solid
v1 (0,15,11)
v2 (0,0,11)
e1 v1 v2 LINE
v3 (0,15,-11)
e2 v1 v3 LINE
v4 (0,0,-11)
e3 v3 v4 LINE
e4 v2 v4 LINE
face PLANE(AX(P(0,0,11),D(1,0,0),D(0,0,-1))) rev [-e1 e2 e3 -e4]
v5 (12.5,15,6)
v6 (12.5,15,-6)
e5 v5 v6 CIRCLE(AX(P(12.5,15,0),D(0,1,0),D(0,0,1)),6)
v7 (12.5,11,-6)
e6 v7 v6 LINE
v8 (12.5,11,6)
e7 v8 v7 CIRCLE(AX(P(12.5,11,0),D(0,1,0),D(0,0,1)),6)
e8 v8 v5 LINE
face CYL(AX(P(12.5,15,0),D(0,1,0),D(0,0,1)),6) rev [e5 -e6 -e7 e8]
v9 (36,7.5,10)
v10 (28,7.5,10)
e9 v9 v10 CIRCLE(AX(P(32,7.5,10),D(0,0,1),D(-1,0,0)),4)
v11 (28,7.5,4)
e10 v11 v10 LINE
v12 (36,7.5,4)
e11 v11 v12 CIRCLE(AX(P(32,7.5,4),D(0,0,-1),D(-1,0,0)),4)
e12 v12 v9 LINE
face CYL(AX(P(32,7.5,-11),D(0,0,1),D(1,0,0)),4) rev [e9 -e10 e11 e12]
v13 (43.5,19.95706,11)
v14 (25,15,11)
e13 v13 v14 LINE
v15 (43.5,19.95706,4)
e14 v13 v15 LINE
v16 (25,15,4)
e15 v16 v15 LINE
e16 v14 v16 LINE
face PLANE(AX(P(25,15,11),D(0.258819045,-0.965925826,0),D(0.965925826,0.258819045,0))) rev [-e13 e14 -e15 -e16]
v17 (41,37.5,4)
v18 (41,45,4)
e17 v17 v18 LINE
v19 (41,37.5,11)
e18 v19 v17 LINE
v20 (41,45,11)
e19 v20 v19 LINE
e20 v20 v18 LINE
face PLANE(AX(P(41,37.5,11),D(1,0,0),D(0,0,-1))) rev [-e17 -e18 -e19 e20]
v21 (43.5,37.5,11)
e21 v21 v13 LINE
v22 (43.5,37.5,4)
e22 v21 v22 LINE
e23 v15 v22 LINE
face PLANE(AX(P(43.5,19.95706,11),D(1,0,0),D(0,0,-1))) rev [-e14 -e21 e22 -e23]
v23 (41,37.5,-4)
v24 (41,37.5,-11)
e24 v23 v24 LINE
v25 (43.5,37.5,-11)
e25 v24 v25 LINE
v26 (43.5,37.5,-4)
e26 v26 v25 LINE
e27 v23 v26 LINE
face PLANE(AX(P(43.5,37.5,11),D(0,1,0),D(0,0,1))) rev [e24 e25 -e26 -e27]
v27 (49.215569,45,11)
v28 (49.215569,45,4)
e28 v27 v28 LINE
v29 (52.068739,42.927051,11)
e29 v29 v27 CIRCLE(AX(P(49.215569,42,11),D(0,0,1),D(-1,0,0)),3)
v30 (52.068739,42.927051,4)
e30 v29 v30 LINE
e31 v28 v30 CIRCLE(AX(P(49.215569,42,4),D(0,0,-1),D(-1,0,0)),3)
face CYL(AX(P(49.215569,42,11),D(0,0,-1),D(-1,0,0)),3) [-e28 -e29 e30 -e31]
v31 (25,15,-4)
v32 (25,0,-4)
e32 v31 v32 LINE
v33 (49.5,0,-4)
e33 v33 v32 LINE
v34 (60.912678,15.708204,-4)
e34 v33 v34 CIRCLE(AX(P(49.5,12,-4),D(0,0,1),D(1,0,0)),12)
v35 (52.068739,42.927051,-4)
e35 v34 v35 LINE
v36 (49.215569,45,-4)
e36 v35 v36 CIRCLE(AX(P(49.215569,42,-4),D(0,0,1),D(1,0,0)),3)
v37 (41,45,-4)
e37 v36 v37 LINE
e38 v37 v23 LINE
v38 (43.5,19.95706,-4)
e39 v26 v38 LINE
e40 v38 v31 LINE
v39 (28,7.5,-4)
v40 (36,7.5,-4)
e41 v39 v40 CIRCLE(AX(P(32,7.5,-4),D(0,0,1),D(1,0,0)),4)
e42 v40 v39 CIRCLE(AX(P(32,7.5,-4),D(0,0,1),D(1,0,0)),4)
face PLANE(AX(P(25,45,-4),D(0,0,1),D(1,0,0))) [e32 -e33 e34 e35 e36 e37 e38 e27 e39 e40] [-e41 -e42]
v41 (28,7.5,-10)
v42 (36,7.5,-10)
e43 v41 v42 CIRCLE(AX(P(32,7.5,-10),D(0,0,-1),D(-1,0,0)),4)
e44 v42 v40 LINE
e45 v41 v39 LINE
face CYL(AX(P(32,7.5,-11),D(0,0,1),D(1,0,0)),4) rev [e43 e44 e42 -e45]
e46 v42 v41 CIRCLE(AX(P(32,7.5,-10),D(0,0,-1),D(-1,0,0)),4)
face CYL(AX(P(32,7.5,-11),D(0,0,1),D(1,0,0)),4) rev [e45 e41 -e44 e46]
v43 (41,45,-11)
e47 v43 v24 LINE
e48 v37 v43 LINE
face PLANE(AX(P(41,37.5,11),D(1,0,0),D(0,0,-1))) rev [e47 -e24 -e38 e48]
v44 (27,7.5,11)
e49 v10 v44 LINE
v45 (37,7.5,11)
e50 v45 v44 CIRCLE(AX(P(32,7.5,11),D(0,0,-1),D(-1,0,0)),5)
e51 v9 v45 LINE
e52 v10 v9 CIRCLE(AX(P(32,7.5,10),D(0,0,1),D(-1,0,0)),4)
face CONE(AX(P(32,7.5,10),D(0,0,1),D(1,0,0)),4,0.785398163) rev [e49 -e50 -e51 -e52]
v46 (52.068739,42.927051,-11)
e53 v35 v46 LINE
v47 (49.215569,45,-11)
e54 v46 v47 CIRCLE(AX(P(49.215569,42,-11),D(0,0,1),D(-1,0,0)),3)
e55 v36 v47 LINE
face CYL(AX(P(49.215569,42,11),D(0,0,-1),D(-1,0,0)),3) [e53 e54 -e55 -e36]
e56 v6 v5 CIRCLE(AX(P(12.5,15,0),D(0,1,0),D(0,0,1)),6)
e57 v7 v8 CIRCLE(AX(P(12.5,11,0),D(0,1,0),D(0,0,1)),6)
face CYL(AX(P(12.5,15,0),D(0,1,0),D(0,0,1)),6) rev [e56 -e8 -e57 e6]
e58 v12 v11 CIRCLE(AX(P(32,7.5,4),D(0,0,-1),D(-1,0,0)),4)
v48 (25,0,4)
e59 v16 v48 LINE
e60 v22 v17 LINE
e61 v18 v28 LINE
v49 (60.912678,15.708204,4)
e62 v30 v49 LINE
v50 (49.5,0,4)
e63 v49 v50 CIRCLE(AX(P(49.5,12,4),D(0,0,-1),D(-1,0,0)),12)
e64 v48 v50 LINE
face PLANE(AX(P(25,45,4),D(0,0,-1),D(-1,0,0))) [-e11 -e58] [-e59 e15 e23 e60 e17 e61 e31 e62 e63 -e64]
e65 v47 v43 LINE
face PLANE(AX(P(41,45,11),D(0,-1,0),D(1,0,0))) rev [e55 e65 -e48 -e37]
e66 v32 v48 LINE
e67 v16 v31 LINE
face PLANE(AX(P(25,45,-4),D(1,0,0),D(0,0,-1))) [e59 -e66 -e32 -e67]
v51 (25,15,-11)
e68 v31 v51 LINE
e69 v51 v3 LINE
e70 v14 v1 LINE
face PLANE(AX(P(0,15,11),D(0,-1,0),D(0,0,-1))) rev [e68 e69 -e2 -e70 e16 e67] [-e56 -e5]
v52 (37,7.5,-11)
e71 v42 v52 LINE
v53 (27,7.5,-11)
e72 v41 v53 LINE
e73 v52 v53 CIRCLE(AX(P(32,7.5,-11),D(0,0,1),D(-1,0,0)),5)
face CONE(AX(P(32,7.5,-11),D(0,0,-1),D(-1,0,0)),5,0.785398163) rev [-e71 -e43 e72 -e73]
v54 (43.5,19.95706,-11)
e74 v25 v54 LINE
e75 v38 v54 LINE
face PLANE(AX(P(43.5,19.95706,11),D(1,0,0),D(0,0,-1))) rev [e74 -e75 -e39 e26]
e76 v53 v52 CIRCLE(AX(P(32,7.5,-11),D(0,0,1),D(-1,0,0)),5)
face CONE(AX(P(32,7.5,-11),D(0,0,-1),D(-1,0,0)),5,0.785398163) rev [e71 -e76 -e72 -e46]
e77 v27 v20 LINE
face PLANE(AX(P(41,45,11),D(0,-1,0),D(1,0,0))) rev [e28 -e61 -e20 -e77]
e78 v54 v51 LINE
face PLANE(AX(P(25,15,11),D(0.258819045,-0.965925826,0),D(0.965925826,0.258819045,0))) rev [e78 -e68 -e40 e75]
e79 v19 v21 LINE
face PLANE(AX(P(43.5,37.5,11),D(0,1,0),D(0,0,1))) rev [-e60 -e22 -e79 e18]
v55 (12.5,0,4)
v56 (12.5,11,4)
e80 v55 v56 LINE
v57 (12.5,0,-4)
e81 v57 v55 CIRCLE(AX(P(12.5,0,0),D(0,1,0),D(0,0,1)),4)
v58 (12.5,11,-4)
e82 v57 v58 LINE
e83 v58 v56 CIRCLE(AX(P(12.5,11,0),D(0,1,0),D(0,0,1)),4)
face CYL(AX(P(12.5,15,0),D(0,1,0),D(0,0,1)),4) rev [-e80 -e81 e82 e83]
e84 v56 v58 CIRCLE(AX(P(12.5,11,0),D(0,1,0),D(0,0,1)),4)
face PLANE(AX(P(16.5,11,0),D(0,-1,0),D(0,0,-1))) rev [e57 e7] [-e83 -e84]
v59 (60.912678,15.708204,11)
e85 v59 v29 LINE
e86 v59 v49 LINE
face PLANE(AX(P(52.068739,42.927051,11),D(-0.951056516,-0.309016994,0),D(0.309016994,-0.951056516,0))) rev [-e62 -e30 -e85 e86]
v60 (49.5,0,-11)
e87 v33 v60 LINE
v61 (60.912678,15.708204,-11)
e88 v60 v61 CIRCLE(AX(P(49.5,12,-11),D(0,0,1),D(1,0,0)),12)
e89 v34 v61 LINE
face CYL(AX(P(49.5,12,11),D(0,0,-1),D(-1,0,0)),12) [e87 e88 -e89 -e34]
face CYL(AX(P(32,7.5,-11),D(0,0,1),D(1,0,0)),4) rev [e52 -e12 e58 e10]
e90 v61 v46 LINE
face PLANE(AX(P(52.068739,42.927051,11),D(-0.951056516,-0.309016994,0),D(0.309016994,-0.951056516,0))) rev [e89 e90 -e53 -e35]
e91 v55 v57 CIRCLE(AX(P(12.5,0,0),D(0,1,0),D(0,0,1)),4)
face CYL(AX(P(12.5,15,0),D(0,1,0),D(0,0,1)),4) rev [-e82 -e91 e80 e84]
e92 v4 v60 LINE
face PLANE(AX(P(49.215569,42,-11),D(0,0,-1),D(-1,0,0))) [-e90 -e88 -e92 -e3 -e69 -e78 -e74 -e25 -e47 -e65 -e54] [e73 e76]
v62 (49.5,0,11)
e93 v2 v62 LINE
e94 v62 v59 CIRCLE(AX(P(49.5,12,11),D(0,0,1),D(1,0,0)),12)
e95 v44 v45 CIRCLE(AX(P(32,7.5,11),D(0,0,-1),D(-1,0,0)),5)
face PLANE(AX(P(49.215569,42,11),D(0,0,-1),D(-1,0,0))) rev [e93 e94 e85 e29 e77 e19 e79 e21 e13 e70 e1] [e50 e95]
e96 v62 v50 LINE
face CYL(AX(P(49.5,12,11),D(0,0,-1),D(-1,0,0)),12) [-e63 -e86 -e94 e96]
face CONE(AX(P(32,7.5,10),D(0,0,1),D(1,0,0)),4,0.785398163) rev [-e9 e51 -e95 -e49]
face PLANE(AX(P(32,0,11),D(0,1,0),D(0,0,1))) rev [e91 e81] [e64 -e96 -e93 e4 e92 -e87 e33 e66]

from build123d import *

# Parameters (mm, degrees)
BRACKET_BODY_DEPTH                = 11
FORK_SLOT_SKETCH_W                = 36.5
FORK_SLOT_SKETCH_H                = 8
FORK_SLOT_8MM_DEPTH               = 77.995129716
MOUNTING_HOLE_CBORE_8_D           = 8
MOUNTING_HOLE_CBORE_8_CBORE_D     = 12
MOUNTING_HOLE_CBORE_8_CBORE_DEPTH = 4
CROSS_HOLE_SKETCH_R               = 4
CROSS_HOLE_8_DEPTH                = 80.317400361
CROSS_HOLE_CHAMFER_1MM_SIZE       = 1


with BuildPart() as part:
    # Bracket Profile Sketch → Bracket Body (new, symmetric)
    with BuildSketch(Plane.XY):
        with BuildLine():
            Line((0, 0), (32, 0))
            Line((32, 0), (49.5, 0))
            ThreePointArc((49.5, 0), (59.208203932, 4.946576972), (60.912678196, 15.708203932))
            Line((60.912678196, 15.708203932), (52.06873868, 42.927050983))
            ThreePointArc((52.06873868, 42.927050983), (50.978924888, 44.427050983), (49.215569131, 45))
            Line((49.215569131, 45), (41, 45))
            Line((41, 45), (41, 37.5))
            Line((41, 37.5), (43.5, 37.5))
            Line((43.5, 37.5), (43.5, 19.95706006))
            Line((43.5, 19.95706006), (25, 15))
            Line((25, 15), (0, 15))
            Line((0, 15), (0, 0))
        make_face()
    extrude(amount=BRACKET_BODY_DEPTH, both=True)

    # Fork Slot Sketch → Fork Slot 8mm (cut, through all)
    with BuildSketch(Plane(origin=(0, 0, 0), x_dir=(1, 0, 0), z_dir=(0, 1, 0))):
        with Locations((43.25, 0)):
            Rectangle(FORK_SLOT_SKETCH_W, FORK_SLOT_SKETCH_H)
    extrude(amount=FORK_SLOT_8MM_DEPTH, mode=Mode.SUBTRACT)

    # Mounting Hole CBore Ø8 (through all)
    with Locations(Plane(origin=(12.5, 15, 0), x_dir=(0, 0, 1), z_dir=(0, 1, 0))):
        with Locations((0, 0)):
            CounterBoreHole(MOUNTING_HOLE_CBORE_8_D / 2, MOUNTING_HOLE_CBORE_8_CBORE_D / 2, MOUNTING_HOLE_CBORE_8_CBORE_DEPTH)

    # Cross Hole Sketch → Cross Hole Ø8 (cut, through all)
    with BuildSketch(Plane.XY.offset(11)):
        with Locations((32, 7.5)):
            Circle(CROSS_HOLE_SKETCH_R)
    extrude(amount=-CROSS_HOLE_8_DEPTH, mode=Mode.SUBTRACT)

    # Cross Hole Chamfer 1mm
    cross_hole_chamfer_1mm_edges = [part.edges().sort_by_distance(p)[0] for p in [
        (28, 7.5, -11),
        (28, 7.5, 11),
    ]]
    chamfer(cross_hole_chamfer_1mm_edges, length=CROSS_HOLE_CHAMFER_1MM_SIZE)


solid = part.part
